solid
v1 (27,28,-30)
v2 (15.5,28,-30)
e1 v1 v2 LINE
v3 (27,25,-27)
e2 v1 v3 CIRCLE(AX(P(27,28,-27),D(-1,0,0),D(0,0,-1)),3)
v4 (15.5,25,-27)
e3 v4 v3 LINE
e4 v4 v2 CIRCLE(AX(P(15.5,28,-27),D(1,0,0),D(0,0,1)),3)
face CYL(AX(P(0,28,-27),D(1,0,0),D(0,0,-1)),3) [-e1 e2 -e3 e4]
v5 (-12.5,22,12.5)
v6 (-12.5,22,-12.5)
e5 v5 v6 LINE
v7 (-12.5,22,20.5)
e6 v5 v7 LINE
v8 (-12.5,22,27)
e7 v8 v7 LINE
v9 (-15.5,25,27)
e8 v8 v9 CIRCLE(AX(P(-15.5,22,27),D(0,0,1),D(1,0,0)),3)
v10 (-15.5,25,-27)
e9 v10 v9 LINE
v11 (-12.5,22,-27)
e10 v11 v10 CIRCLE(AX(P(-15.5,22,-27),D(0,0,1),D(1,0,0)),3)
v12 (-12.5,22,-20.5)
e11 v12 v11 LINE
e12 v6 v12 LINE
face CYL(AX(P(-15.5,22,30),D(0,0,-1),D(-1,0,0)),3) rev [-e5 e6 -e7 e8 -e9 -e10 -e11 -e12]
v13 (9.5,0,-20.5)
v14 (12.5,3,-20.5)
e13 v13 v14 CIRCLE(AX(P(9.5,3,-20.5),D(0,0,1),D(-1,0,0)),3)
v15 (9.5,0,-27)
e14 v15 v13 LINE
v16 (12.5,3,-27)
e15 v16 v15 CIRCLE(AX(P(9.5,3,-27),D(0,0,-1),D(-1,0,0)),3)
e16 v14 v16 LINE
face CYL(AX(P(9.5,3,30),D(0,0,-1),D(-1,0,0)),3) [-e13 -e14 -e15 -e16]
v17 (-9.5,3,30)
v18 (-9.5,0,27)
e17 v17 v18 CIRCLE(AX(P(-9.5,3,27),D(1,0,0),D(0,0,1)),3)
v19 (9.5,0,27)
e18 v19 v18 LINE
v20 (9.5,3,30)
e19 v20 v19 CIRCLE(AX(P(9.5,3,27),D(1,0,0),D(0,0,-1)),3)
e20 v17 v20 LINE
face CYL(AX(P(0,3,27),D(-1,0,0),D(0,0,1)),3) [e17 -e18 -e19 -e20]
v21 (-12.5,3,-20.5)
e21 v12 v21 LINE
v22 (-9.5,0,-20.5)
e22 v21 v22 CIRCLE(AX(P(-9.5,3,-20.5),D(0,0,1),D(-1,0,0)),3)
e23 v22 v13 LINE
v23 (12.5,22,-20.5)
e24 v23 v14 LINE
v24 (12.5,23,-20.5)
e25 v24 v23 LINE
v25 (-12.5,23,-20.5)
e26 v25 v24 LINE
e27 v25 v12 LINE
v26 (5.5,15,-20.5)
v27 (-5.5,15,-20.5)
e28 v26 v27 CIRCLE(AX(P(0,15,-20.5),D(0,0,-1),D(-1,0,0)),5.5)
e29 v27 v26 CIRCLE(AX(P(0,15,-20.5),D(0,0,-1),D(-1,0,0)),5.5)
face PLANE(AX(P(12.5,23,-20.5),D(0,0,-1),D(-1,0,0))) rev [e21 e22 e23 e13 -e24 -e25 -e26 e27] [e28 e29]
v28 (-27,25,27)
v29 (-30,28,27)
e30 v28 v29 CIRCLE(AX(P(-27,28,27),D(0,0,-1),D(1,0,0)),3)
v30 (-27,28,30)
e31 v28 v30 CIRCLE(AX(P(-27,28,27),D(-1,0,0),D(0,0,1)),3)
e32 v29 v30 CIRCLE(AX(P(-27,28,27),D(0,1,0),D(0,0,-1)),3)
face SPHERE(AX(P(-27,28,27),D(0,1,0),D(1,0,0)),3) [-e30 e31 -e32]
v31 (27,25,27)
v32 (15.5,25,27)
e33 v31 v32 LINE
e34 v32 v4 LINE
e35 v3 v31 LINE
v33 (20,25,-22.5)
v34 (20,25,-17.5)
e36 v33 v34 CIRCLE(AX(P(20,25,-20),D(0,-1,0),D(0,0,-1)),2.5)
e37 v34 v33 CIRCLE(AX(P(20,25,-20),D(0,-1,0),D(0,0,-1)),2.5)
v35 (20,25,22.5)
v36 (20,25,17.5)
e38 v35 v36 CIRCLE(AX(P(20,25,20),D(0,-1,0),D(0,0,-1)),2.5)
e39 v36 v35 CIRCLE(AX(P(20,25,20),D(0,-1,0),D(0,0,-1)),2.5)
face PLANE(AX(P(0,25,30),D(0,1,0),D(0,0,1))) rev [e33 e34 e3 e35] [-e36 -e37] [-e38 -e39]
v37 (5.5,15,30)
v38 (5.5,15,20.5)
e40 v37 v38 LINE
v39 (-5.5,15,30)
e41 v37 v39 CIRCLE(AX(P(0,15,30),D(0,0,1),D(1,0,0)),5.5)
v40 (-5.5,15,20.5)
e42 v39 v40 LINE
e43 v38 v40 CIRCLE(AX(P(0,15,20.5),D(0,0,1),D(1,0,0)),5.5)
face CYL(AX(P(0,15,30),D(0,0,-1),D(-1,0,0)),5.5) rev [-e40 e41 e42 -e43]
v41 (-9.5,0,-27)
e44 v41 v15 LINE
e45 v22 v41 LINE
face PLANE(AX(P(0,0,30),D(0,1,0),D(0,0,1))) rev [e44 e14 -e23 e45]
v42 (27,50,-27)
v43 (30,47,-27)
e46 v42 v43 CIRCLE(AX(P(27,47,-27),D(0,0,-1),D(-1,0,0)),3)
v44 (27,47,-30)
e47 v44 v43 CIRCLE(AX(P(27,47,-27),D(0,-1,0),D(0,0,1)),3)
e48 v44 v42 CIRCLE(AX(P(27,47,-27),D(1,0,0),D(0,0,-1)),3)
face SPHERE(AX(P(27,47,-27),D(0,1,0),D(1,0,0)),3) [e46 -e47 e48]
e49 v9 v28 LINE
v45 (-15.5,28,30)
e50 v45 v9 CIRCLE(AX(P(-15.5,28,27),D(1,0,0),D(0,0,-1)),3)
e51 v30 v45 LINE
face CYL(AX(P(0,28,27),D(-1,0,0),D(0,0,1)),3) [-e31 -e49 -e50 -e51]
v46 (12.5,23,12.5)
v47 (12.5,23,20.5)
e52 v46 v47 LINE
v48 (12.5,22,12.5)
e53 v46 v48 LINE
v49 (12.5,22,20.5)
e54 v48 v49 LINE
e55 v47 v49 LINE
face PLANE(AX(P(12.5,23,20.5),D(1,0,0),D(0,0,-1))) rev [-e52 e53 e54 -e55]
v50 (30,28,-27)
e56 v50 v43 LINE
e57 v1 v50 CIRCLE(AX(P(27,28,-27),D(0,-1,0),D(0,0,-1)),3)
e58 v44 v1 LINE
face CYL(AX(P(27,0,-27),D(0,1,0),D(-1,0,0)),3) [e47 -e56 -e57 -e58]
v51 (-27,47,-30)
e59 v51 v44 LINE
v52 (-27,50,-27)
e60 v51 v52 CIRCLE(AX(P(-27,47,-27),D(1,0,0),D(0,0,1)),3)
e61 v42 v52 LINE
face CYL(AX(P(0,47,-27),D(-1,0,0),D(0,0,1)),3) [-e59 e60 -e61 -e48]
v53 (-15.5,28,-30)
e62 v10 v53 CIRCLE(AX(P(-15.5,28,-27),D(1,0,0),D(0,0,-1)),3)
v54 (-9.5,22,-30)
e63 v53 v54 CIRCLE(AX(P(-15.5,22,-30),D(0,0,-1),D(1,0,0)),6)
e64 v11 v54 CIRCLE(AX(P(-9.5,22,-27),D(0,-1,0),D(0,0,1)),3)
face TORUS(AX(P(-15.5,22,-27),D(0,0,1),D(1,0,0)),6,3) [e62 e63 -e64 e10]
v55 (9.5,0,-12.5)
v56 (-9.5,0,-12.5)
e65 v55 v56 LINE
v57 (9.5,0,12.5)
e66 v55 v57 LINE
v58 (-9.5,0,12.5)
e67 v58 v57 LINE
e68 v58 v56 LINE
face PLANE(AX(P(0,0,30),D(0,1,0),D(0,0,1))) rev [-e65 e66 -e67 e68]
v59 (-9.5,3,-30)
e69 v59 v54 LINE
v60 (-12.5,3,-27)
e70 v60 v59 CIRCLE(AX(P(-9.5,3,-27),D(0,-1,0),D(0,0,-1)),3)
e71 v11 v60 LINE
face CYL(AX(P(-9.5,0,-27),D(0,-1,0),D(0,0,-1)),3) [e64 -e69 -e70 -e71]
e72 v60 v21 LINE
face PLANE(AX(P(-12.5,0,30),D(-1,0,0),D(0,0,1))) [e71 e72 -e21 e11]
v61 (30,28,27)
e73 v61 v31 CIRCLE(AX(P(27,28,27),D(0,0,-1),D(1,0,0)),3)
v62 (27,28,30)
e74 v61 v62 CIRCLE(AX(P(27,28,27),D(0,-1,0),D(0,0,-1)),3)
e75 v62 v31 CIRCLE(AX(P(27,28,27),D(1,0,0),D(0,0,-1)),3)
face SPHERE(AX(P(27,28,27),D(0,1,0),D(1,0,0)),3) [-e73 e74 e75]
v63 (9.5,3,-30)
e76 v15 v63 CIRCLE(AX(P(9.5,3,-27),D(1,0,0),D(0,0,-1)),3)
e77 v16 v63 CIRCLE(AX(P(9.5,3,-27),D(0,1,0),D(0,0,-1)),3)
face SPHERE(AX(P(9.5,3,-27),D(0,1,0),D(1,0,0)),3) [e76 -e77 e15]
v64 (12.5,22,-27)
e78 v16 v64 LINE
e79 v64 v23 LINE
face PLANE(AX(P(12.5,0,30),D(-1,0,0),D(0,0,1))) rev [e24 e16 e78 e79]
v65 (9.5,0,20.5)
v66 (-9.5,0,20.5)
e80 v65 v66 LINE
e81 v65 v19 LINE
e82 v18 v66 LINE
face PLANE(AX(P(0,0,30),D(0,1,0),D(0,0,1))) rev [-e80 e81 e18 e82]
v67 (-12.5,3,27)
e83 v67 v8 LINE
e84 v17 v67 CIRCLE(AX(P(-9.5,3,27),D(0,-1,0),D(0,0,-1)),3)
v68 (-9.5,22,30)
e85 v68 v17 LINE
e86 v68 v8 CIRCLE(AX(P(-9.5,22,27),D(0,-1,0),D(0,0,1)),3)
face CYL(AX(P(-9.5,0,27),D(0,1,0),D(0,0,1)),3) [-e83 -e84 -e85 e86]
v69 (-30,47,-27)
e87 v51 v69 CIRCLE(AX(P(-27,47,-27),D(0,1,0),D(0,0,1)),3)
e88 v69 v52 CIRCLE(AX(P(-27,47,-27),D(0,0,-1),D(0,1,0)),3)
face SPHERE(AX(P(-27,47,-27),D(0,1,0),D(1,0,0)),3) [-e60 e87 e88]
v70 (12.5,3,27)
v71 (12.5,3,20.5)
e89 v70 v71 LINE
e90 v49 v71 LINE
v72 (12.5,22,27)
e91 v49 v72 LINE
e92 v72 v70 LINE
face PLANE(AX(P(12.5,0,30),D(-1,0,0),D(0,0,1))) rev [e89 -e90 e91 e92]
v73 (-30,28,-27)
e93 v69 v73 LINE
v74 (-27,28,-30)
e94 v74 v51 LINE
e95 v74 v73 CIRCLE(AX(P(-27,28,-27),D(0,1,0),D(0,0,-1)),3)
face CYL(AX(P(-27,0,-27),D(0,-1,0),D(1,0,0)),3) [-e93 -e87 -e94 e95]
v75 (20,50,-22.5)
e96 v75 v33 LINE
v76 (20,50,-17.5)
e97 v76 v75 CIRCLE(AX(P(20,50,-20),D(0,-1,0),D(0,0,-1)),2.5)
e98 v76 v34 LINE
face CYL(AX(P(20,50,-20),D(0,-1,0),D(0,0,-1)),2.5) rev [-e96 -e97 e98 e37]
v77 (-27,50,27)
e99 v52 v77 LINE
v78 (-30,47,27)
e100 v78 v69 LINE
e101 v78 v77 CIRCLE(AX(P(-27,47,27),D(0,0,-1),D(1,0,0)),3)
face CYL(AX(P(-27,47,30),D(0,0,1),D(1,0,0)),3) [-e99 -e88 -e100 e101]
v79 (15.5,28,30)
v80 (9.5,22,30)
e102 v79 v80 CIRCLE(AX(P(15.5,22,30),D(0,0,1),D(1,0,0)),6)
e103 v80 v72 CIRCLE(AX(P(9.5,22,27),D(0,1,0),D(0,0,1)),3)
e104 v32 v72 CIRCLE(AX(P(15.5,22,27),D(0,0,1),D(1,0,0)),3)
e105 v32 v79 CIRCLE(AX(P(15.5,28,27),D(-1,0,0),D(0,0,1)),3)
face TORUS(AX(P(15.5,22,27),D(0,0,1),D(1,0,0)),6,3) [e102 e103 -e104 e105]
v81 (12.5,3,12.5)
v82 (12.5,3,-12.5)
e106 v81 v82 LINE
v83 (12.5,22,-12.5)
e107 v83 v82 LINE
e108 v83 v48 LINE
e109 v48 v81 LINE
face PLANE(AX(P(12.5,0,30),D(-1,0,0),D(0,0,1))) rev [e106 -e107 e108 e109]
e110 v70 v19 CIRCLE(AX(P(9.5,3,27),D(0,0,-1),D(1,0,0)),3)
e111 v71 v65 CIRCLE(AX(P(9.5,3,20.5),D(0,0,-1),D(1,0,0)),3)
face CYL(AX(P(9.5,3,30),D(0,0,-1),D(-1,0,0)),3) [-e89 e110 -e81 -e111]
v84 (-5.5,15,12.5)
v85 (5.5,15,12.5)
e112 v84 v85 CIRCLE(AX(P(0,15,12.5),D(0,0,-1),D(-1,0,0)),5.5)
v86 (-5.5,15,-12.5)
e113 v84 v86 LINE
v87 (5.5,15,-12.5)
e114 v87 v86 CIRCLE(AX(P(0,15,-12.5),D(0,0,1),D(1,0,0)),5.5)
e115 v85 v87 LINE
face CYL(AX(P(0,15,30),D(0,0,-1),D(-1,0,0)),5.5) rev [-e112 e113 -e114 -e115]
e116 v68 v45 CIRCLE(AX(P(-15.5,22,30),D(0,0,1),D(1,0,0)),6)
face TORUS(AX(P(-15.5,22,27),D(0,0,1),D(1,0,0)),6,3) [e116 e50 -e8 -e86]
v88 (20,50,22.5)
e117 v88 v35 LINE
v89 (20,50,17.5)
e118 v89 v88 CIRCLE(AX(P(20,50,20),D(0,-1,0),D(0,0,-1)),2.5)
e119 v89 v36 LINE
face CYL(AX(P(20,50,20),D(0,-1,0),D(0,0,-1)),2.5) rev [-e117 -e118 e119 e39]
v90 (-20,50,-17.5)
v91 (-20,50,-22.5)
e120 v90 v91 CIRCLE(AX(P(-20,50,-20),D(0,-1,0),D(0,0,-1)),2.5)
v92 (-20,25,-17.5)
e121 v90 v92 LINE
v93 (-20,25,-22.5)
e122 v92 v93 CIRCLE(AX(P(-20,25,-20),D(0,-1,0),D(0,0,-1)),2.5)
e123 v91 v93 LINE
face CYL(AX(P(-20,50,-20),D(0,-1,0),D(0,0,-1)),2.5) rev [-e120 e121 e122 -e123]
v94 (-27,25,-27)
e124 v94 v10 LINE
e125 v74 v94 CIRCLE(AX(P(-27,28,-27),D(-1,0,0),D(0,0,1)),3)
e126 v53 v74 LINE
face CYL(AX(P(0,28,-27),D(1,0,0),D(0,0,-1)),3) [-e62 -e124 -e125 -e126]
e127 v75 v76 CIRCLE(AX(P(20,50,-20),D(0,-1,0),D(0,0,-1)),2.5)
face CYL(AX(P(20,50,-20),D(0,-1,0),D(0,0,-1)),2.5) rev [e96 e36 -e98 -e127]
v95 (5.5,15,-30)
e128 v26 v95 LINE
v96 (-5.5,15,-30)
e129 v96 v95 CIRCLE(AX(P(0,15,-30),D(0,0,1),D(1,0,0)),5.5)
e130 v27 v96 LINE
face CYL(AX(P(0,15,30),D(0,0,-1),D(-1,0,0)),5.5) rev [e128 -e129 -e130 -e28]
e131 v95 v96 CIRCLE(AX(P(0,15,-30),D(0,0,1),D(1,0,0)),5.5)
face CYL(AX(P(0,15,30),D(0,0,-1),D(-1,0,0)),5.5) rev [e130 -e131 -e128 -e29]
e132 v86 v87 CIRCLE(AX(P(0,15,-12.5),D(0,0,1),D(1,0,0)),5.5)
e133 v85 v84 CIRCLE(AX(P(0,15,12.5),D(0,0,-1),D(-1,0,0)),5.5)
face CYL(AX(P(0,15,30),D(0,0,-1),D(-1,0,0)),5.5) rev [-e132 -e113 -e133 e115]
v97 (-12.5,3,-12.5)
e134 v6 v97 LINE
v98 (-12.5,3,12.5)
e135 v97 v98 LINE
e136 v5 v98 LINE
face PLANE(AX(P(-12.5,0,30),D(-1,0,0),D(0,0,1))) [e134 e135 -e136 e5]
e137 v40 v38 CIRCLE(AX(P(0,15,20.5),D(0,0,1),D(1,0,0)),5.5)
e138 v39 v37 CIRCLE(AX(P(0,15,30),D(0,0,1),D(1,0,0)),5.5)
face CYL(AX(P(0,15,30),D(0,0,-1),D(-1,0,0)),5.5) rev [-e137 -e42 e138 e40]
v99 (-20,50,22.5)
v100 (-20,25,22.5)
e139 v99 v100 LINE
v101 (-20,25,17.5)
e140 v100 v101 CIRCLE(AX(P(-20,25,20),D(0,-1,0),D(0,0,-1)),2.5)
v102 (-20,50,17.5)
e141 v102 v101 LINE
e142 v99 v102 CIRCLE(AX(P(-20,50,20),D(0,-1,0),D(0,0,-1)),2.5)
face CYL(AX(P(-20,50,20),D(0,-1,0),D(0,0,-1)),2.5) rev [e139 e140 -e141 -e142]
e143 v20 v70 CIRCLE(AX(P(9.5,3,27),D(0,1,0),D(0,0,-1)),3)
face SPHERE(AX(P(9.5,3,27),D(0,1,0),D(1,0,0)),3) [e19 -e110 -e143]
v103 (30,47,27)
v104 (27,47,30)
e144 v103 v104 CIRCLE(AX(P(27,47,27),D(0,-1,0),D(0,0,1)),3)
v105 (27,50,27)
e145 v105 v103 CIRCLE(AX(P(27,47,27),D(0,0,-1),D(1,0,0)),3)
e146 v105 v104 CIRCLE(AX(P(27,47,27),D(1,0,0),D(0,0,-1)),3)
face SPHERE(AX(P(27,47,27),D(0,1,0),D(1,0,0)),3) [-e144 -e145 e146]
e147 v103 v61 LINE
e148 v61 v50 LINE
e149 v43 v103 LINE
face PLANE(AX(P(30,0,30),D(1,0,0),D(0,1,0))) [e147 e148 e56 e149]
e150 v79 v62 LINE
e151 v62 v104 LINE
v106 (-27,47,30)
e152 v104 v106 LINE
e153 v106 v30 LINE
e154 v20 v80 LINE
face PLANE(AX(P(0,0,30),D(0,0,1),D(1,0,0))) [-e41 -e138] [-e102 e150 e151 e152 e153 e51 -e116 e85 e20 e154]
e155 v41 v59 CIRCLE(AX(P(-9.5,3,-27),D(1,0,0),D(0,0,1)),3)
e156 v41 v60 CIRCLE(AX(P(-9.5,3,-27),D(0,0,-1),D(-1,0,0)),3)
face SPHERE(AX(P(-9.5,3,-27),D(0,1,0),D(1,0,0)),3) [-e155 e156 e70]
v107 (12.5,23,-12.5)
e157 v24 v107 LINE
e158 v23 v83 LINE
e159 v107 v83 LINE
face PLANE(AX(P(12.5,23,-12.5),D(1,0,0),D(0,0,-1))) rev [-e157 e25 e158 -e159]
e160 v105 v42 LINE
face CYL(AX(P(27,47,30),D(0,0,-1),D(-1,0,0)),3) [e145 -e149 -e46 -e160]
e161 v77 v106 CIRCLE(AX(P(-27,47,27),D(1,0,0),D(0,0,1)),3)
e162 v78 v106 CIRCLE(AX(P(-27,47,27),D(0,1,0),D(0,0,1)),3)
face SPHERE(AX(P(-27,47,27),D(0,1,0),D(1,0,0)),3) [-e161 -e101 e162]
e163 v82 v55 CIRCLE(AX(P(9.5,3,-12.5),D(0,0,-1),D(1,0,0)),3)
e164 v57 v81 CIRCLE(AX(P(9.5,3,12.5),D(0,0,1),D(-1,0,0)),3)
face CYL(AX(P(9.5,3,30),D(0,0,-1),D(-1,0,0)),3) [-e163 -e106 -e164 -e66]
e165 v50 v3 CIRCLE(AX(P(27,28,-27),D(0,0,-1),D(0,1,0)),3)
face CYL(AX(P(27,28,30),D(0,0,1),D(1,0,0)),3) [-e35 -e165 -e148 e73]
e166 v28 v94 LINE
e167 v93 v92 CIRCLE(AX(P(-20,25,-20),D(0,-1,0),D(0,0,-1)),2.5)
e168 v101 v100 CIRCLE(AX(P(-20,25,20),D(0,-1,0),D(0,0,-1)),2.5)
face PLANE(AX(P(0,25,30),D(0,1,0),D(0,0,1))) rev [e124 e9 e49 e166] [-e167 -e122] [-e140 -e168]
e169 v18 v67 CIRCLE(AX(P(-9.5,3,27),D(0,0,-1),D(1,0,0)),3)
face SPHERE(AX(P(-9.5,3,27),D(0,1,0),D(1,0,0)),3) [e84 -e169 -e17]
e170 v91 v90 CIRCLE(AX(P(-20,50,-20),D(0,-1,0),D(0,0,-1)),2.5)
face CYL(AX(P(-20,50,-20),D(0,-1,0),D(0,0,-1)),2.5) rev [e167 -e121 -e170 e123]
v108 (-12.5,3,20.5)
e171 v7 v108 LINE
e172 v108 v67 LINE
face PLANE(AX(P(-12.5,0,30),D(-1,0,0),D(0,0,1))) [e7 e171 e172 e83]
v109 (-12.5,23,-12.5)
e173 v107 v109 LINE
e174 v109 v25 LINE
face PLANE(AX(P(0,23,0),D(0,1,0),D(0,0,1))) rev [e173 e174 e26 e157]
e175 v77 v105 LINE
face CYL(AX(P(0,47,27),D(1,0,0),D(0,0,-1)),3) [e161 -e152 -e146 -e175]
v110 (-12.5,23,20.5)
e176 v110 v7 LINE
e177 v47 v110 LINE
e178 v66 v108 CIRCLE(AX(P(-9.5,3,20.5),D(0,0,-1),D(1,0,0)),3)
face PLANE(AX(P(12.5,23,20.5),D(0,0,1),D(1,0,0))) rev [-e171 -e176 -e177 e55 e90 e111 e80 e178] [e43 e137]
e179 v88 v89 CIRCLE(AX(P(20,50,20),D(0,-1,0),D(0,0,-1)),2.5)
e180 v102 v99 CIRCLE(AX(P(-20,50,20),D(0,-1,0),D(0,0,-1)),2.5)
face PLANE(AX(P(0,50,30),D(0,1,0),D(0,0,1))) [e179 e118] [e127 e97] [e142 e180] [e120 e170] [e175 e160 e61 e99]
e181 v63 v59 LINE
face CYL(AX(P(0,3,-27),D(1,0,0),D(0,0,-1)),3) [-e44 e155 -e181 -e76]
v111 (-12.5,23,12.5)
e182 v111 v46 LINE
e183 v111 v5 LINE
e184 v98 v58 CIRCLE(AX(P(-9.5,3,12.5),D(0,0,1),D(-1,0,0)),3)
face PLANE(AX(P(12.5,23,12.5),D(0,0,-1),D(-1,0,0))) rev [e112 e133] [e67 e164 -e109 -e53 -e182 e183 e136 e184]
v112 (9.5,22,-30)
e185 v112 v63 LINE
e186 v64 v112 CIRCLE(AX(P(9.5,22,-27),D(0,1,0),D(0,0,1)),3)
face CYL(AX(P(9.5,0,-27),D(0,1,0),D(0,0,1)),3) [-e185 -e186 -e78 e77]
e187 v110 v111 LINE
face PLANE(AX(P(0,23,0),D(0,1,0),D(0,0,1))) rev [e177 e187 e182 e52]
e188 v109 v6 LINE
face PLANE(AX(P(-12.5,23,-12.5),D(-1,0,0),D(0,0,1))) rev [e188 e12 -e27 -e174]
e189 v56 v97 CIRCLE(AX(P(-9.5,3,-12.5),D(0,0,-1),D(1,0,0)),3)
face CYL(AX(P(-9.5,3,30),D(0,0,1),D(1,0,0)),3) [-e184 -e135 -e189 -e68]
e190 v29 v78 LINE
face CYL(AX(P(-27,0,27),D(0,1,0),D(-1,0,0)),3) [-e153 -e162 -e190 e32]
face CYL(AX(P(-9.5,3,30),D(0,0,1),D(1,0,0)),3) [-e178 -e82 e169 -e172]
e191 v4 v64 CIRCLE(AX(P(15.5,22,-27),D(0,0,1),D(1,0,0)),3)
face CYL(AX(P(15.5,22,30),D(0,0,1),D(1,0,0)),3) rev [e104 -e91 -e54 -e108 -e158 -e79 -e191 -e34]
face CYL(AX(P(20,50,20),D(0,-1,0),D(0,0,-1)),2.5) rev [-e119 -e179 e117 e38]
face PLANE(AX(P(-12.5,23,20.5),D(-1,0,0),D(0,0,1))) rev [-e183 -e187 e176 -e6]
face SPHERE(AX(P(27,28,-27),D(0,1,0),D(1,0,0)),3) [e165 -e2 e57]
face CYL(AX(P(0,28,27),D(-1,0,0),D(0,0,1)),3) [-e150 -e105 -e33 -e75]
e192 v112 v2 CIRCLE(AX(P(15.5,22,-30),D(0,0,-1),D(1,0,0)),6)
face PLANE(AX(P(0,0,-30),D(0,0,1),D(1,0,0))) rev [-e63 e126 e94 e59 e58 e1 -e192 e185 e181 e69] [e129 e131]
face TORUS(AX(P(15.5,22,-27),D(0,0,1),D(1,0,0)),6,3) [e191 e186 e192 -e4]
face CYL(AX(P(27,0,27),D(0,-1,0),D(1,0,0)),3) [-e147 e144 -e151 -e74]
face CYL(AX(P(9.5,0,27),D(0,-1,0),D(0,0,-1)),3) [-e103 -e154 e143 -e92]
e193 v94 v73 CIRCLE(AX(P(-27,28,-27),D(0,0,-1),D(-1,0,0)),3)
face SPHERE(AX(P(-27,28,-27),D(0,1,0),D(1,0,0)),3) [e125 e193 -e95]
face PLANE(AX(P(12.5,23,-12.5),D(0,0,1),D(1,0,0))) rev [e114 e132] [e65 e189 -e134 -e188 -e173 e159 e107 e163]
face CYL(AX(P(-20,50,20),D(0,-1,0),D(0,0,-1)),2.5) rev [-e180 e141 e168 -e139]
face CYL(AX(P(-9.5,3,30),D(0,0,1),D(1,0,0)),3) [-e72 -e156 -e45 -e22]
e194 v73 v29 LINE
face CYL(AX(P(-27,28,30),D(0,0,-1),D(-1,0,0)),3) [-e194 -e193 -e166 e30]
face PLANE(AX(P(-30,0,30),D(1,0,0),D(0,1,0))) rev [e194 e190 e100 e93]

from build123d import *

# Parameters (mm, degrees)
SKETCH1_W           = 17.5
SKETCH1_H           = 25
SKETCH1_W_2         = 12.5
BOSS_EXTRUDE1_DEPTH = 30
FILLET1_R           = 3
SKETCH2_W           = 25
SKETCH2_H           = 8
CUT_EXTRUDE1_DEPTH  = 23
SKETCH3_R           = 2.5
CUT_EXTRUDE2_DEPTH  = 50.244289009


with BuildPart() as part:
    # Sketch1 → Boss-Extrude1 (new, symmetric)
    with BuildSketch(Plane.XY):
        with BuildLine():
            Line((-12.5, 0), (0, 0))
            Line((0, 0), (0, 9.5))
            ThreePointArc((0, 9.5), (-5.5, 15), (0, 20.5))
            Line((0, 20.5), (0, 25))
            Line((0, 25), (-12.5, 25))
            Line((-12.5, 25), (-12.5, 0))
        make_face()
        with BuildLine():
            Line((0, 9.5), (0, 0))
            Line((0, 0), (12.5, 0))
            Line((12.5, 0), (12.5, 25))
            Line((12.5, 25), (0, 25))
            Line((0, 25), (0, 20.5))
            ThreePointArc((0, 20.5), (3.889087297, 18.889087297), (5.5, 15))
            ThreePointArc((5.5, 15), (3.889087297, 11.110912703), (0, 9.5))
        make_face()
        with Locations((21.25, 37.5)):
            Rectangle(SKETCH1_W, SKETCH1_H)
        with Locations((6.25, 37.5)):
            Rectangle(SKETCH1_W_2, SKETCH1_H)
        with Locations((-6.25, 37.5)):
            Rectangle(SKETCH1_W_2, SKETCH1_H)
        with Locations((-21.25, 37.5)):
            Rectangle(SKETCH1_W, SKETCH1_H)
    extrude(amount=BOSS_EXTRUDE1_DEPTH, both=True)

    # Fillet1
    fillet1_edges = [part.edges().sort_by_distance(p)[0] for p in [
        (0, 0, -30),
        (-12.5, 12.5, -30),
        (-21.25, 25, -30),
        (-30, 37.5, -30),
        (30, 37.5, 30),
        (0, 50, -30),
        (30, 37.5, -30),
        (21.25, 25, -30),
        (12.5, 12.5, -30),
        (0, 50, 30),
        (12.5, 0, 0),
        (-12.5, 0, 0),
        (-12.5, 25, 0),
        (-30, 25, 0),
        (-30, 50, 0),
        (30, 50, 0),
        (30, 25, 0),
        (12.5, 25, 0),
        (-30, 37.5, 30),
        (-21.25, 25, 30),
        (-12.5, 12.5, 30),
        (0, 0, 30),
        (12.5, 12.5, 30),
        (21.25, 25, 30),
    ]]
    fillet(fillet1_edges, radius=FILLET1_R)

    # Sketch2 → Cut-Extrude1 (cut)
    with BuildSketch(Plane.XZ):
        with Locations((0, 16.5)):
            Rectangle(SKETCH2_W, SKETCH2_H)
        with Locations((0, -16.5)):
            Rectangle(SKETCH2_W, SKETCH2_H)
    extrude(amount=-CUT_EXTRUDE1_DEPTH, mode=Mode.SUBTRACT)

    # Sketch3 → Cut-Extrude2 (cut, through all)
    with BuildSketch(Plane.XZ.offset(-25)):
        with Locations(Location((20, 20, 0), (0, 0, 270))):
            Circle(SKETCH3_R)
        with Locations(Location((20, -20, 0), (0, 0, 270))):
            Circle(SKETCH3_R)
        with Locations(Location((-20, -20, 0), (0, 0, 270))):
            Circle(SKETCH3_R)
        with Locations(Location((-20, 20, 0), (0, 0, 270))):
            Circle(SKETCH3_R)
    extrude(amount=-CUT_EXTRUDE2_DEPTH, mode=Mode.SUBTRACT)


solid = part.part
